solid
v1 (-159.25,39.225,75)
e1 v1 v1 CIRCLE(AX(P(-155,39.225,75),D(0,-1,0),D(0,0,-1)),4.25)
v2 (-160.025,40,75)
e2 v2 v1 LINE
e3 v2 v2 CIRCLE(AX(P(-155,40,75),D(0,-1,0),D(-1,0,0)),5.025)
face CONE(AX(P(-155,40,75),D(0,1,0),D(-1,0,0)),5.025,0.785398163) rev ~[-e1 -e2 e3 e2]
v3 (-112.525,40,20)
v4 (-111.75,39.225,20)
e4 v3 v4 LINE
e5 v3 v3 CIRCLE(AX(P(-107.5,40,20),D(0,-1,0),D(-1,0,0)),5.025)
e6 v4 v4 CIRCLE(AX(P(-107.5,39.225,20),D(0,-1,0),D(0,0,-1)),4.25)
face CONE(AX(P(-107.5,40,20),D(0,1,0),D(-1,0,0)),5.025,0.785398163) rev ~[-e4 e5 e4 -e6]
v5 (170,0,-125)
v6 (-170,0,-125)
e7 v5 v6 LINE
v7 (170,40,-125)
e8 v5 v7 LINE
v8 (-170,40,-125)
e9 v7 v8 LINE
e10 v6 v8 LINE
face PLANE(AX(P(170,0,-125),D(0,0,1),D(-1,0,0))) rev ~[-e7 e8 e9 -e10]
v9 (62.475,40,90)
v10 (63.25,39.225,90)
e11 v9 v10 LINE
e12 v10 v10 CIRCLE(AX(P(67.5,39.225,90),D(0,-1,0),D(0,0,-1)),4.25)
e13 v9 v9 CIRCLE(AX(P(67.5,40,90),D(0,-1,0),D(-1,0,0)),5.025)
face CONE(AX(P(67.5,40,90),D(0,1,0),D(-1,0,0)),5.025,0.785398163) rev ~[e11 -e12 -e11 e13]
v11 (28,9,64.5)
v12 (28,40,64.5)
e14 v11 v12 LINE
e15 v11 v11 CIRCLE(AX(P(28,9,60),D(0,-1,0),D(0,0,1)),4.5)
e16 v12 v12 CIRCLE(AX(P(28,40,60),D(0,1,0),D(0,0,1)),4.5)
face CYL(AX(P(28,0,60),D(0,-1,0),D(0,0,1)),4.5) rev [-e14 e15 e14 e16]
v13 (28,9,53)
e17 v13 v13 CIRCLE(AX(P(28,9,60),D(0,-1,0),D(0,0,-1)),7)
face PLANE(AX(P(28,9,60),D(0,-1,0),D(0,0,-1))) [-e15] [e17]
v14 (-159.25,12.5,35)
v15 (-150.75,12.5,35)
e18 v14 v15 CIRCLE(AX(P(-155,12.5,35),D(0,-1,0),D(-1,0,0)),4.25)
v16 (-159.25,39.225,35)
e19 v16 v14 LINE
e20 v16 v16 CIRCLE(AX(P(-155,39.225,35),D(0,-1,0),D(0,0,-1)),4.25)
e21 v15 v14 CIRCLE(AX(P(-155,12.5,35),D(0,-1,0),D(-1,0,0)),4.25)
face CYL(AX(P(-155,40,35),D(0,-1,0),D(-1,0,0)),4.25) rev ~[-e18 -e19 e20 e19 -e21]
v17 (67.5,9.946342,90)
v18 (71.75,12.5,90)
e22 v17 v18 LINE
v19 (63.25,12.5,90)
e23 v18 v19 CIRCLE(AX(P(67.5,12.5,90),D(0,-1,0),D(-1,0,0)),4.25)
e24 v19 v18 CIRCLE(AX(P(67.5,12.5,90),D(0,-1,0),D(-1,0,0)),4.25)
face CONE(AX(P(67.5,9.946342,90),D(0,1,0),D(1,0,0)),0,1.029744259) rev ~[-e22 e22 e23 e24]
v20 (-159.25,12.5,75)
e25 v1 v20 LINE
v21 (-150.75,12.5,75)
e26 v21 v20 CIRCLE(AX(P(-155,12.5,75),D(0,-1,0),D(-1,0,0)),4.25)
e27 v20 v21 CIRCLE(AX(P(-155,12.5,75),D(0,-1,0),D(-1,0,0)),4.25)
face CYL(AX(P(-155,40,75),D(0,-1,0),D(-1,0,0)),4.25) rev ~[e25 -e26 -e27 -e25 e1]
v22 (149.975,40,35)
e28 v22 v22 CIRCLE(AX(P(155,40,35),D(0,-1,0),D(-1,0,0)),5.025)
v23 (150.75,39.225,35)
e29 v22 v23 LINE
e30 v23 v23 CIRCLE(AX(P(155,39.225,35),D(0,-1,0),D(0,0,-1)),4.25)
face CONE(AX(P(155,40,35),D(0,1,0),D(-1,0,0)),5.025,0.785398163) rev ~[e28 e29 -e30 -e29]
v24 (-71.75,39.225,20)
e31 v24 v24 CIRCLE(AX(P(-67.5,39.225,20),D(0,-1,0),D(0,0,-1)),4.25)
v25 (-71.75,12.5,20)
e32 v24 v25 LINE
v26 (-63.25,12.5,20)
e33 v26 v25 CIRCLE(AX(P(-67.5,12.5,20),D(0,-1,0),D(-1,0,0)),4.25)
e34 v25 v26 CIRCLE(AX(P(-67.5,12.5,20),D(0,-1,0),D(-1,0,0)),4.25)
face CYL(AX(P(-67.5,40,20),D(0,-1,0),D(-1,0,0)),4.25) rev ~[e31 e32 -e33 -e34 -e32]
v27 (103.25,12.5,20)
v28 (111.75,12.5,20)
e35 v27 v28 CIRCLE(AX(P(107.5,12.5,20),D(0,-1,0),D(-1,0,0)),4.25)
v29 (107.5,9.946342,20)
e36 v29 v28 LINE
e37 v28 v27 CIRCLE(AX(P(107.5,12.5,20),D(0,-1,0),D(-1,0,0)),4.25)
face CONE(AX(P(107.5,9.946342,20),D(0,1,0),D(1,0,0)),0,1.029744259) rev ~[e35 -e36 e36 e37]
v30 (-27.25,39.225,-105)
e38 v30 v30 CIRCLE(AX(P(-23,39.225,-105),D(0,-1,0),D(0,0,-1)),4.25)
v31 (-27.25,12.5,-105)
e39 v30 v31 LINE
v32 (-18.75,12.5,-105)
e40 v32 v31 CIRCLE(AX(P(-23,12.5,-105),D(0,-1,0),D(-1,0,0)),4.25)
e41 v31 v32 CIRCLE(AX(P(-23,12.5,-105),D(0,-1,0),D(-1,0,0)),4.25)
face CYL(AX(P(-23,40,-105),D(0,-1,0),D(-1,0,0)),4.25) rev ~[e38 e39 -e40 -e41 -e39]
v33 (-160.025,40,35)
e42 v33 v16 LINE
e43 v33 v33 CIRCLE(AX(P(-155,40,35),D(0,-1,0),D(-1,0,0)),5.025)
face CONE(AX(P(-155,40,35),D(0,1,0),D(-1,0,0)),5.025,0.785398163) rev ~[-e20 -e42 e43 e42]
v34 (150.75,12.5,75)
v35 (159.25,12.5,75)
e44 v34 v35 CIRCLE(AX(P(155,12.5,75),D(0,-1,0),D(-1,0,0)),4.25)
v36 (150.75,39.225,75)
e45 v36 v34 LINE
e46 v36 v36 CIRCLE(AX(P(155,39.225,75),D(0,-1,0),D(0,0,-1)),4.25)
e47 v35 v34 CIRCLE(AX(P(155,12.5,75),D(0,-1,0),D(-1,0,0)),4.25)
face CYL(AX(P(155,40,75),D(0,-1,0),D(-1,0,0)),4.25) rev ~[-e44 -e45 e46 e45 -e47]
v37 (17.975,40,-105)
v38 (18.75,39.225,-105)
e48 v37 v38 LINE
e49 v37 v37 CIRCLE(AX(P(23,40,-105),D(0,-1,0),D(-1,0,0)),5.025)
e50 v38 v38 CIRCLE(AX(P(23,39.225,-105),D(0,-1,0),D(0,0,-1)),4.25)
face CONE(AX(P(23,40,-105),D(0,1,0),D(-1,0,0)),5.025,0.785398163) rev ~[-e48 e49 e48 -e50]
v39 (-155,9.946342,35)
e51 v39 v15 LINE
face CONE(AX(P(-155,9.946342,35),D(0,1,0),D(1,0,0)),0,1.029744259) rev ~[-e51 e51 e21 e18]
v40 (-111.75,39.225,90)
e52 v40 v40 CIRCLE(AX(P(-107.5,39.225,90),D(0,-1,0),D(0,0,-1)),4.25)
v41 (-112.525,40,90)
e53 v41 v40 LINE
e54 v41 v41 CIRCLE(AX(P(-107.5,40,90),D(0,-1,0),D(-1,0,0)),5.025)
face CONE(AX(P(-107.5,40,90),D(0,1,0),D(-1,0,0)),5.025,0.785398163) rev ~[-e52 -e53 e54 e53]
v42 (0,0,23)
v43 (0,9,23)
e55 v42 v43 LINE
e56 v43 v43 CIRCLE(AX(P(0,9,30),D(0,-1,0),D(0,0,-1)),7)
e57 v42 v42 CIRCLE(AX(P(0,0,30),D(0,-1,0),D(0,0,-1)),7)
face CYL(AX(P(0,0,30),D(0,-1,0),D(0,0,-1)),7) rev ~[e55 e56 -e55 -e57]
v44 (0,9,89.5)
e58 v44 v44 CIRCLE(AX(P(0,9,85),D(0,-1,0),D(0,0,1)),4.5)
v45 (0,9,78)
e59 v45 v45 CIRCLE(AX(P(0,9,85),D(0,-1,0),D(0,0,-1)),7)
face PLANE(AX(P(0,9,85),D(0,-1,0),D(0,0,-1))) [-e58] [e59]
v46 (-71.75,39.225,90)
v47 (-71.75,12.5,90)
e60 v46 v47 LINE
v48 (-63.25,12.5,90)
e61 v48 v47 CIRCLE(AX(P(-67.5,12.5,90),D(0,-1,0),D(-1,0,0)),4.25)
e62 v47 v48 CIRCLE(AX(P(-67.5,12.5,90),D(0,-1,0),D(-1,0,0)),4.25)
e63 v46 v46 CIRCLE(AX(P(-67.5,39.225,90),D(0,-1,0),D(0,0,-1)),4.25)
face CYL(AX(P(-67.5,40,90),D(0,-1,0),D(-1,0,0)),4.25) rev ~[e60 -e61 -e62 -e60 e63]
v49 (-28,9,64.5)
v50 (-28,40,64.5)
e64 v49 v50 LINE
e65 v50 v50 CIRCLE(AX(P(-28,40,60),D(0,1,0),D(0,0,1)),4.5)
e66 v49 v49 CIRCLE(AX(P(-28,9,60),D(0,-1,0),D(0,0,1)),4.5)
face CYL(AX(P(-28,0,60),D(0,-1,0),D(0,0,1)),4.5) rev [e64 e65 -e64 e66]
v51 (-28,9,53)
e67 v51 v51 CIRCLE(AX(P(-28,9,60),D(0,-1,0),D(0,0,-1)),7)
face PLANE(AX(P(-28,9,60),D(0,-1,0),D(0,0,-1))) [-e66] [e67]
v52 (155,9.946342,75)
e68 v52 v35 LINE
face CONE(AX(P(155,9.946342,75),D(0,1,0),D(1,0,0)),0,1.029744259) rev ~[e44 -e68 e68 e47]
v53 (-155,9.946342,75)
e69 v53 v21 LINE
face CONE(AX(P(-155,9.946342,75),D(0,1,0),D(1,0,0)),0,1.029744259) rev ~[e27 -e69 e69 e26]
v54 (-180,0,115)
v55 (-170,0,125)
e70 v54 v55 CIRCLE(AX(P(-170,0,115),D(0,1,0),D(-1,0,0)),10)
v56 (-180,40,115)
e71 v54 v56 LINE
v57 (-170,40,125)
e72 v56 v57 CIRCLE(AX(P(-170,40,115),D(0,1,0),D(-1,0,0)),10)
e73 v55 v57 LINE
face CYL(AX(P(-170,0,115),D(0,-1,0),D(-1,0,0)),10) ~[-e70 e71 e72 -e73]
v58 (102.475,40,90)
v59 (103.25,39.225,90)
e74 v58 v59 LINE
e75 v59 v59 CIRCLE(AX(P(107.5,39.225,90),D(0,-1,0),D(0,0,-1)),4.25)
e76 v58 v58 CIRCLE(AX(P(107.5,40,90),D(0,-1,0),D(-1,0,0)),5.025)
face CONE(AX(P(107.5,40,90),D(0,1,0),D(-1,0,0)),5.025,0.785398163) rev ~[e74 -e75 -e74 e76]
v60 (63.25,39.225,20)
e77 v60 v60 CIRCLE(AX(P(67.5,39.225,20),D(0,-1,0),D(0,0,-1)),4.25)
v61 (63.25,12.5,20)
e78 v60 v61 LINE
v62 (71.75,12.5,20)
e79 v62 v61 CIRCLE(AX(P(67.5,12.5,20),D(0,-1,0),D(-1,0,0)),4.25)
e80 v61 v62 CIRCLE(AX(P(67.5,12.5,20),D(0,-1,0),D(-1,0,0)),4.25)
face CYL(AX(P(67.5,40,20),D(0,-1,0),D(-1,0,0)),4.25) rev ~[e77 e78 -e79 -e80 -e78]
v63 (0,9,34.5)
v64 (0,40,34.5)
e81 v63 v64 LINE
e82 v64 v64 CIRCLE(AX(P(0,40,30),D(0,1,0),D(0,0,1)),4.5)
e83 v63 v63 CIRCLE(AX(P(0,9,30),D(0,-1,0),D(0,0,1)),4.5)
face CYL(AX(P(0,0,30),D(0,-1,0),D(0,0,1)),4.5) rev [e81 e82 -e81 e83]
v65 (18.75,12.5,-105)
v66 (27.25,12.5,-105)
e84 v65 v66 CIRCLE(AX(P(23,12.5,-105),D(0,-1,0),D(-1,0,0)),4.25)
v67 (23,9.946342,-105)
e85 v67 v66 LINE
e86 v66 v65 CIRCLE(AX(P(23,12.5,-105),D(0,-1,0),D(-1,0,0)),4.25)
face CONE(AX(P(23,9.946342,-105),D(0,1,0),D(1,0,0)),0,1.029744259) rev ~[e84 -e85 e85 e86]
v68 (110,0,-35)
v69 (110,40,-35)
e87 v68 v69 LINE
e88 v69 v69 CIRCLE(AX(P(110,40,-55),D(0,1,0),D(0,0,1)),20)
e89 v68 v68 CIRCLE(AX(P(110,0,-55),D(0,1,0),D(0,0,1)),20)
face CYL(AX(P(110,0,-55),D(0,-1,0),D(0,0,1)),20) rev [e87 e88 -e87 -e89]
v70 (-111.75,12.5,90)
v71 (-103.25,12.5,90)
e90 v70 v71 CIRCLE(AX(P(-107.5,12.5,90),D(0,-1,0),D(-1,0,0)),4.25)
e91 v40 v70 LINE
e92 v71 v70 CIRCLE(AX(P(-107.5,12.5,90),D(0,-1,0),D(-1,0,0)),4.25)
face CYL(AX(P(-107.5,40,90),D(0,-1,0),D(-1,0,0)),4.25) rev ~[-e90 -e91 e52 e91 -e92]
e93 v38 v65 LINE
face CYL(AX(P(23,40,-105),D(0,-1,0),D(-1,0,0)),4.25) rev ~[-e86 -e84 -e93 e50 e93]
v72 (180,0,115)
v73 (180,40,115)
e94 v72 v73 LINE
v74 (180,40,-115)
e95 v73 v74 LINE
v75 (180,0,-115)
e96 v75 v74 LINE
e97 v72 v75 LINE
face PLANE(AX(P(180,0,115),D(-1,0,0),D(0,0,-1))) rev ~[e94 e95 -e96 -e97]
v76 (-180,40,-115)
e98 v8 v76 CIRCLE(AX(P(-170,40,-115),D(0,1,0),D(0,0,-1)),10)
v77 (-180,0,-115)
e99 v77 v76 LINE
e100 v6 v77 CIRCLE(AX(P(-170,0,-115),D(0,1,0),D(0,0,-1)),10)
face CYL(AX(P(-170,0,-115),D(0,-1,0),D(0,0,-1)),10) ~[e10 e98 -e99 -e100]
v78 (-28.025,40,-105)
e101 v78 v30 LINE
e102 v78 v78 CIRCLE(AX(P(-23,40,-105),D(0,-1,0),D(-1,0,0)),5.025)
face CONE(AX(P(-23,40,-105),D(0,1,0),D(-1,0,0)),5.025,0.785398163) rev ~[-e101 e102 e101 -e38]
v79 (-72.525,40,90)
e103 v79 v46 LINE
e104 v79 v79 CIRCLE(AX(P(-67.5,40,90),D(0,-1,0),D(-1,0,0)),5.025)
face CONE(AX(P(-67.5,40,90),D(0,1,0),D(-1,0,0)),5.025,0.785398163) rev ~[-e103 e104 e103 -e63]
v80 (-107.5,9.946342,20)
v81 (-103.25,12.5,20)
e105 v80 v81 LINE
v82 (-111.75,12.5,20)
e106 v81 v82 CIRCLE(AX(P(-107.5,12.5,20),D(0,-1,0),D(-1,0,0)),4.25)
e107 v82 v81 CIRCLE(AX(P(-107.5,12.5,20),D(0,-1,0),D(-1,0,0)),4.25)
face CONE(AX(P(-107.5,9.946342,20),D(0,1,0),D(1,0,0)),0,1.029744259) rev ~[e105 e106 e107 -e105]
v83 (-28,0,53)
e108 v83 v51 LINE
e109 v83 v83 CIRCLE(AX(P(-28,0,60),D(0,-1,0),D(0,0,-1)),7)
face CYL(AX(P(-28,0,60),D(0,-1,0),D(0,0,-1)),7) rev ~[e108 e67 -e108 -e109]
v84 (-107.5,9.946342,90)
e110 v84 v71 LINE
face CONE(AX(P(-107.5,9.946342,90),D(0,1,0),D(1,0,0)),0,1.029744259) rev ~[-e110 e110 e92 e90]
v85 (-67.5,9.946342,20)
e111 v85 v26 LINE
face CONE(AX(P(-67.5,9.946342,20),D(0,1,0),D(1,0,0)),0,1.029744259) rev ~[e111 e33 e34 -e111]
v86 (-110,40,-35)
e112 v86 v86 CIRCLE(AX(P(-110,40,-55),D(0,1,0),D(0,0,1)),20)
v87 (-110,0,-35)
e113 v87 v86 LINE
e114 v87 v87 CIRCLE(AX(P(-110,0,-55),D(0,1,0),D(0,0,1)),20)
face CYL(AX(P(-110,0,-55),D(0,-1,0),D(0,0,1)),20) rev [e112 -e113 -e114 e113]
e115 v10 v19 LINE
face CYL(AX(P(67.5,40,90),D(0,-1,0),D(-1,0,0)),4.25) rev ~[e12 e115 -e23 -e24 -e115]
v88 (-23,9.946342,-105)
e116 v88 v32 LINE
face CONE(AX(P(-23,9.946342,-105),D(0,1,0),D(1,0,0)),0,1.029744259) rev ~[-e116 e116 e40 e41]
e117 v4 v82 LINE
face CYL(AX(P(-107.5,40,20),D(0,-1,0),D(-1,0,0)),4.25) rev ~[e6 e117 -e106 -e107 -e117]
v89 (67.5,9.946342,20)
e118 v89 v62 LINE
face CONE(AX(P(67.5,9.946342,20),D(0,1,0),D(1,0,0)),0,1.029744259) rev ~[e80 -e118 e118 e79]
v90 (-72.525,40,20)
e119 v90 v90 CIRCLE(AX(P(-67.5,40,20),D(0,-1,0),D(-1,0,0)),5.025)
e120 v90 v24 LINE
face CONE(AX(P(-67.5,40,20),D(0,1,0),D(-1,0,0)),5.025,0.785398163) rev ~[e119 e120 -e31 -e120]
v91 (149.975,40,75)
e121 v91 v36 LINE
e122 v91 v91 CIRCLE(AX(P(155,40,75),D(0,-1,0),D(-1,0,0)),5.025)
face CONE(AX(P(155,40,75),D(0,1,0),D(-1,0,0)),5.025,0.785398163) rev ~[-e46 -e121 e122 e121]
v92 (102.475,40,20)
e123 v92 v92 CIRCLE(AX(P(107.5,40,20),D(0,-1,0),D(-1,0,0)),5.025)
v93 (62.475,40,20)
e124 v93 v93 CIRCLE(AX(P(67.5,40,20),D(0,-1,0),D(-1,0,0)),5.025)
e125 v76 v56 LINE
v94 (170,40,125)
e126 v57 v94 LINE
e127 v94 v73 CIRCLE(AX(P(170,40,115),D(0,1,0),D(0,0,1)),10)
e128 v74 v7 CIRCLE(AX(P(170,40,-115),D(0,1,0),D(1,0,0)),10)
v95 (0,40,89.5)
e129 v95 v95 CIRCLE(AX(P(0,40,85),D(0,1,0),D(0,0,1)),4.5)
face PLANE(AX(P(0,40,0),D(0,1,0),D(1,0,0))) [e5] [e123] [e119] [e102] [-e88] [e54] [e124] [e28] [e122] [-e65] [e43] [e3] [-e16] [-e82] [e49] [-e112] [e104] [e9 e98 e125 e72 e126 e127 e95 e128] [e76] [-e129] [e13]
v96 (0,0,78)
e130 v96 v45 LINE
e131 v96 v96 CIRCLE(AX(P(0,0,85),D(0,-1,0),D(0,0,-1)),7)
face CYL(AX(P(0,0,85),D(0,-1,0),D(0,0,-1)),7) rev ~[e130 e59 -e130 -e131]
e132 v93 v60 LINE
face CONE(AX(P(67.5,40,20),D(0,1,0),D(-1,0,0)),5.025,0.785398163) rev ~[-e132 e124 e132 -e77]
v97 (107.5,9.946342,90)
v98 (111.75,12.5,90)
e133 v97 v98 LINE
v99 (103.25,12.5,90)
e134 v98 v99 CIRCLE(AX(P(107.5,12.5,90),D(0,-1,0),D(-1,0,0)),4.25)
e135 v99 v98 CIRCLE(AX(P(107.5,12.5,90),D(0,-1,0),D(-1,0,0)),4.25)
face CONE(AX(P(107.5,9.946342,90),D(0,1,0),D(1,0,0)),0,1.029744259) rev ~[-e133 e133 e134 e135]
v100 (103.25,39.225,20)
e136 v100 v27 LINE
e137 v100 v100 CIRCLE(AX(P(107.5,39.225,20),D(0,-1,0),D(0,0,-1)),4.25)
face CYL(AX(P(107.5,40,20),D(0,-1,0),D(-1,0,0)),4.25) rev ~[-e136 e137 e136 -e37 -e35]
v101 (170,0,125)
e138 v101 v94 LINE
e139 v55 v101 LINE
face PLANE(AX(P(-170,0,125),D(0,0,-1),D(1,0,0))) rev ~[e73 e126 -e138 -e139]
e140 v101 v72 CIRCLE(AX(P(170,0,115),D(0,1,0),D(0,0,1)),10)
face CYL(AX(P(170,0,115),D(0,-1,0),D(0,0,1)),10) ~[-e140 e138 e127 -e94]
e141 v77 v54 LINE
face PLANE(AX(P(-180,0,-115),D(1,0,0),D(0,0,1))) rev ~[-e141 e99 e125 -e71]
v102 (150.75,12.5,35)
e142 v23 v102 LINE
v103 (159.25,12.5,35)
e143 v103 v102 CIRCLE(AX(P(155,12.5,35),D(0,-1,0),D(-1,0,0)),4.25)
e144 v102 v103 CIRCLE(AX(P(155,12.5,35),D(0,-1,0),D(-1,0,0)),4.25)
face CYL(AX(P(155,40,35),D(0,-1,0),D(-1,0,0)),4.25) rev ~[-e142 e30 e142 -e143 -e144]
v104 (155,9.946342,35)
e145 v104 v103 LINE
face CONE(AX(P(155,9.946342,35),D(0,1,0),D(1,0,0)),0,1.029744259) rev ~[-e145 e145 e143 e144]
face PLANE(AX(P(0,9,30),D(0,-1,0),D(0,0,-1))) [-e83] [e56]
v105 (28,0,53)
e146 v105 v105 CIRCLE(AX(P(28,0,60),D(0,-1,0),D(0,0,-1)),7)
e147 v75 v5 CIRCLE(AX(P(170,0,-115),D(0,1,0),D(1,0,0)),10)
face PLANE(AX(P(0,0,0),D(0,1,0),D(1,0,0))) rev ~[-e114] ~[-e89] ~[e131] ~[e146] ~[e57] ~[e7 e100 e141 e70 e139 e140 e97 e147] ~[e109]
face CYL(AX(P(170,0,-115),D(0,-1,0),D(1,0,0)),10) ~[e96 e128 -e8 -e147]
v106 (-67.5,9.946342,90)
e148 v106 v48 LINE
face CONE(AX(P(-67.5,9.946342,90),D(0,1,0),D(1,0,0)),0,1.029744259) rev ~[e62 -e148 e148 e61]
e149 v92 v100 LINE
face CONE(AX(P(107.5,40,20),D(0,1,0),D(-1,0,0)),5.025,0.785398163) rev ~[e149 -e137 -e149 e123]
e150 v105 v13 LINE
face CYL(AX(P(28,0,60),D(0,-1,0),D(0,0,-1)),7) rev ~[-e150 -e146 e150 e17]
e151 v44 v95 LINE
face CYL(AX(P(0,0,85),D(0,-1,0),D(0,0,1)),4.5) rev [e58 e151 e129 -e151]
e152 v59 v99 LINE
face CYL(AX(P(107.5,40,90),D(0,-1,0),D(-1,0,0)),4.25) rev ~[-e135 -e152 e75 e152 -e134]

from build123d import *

# Parameters (mm, degrees)
SKETCH1_R                    = 20
SKETCH1_R_2                  = 4.5
BOSS_EXTRUDE1_DEPTH          = 40
SKETCH2_R                    = 7
CUT_EXTRUDE1_DEPTH           = 9
M10_TAPPED_HOLE1_D           = 8.5
M10_TAPPED_HOLE1_DEPTH       = 27.5
M10_TAPPED_HOLE1_CSINK_D     = 10.05
M10_TAPPED_HOLE1_CSINK_ANGLE = 90
M10_TAPPED_HOLE1_TIP         = 2.553657631


with BuildPart() as part:
    # Sketch1 → Boss-Extrude1 (new body)
    with BuildSketch(Plane(origin=(0, 0, 0), x_dir=(1, 0, 0), z_dir=(0, 1, 0))):
        with BuildLine():
            Line((-170, -125), (170, -125))
            ThreePointArc((170, -125), (177.071067812, -122.071067812), (180, -115))
            Line((180, -115), (180, 115))
            ThreePointArc((180, 115), (177.071067812, 122.071067812), (170, 125))
            Line((170, 125), (-170, 125))
            ThreePointArc((-170, 125), (-177.071067812, 122.071067812), (-180, 115))
            Line((-180, 115), (-180, -115))
            ThreePointArc((-180, -115), (-177.071067812, -122.071067812), (-170, -125))
        make_face()
        with Locations(Location((-110, 55, 0), (0, 0, 270))):
            Circle(SKETCH1_R, mode=Mode.SUBTRACT)
        with Locations(Location((110, 55, 0), (0, 0, 270))):
            Circle(SKETCH1_R, mode=Mode.SUBTRACT)
        with Locations(Location((0, -85, 0), (0, 0, 270))):
            Circle(SKETCH1_R_2, mode=Mode.SUBTRACT)
        with Locations(Location((0, -30, 0), (0, 0, 270))):
            Circle(SKETCH1_R_2, mode=Mode.SUBTRACT)
        with Locations(Location((28, -60, 0), (0, 0, 270))):
            Circle(SKETCH1_R_2, mode=Mode.SUBTRACT)
        with Locations(Location((-28, -60, 0), (0, 0, 270))):
            Circle(SKETCH1_R_2, mode=Mode.SUBTRACT)
    extrude(amount=BOSS_EXTRUDE1_DEPTH)

    # Sketch2 → Cut-Extrude1 (cut)
    with BuildSketch(Plane.XZ):
        with Locations(Location((0, 30, 0), (0, 0, 270))):
            Circle(SKETCH2_R)
        with Locations(Location((-28, 60, 0), (0, 0, 270))):
            Circle(SKETCH2_R)
        with Locations(Location((0, 85, 0), (0, 0, 270))):
            Circle(SKETCH2_R)
        with Locations(Location((28, 60, 0), (0, 0, 270))):
            Circle(SKETCH2_R)
    extrude(amount=-CUT_EXTRUDE1_DEPTH, mode=Mode.SUBTRACT)

    # M10 Tapped Hole1
    with Locations(Plane(origin=(0, 40, 0), x_dir=(1, 0, 0), z_dir=(0, 1, 0))):
        with Locations((-23, 105), (-155, -35), (-155, -75), (-107.5, -20), (-67.5, -20), (-107.5, -90), (-67.5, -90), (155, -75), (155, -35), (67.5, -90), (107.5, -90), (67.5, -20), (107.5, -20), (23, 105)):
            CounterSinkHole(M10_TAPPED_HOLE1_D / 2, M10_TAPPED_HOLE1_CSINK_D / 2, depth=M10_TAPPED_HOLE1_DEPTH, counter_sink_angle=M10_TAPPED_HOLE1_CSINK_ANGLE)
            with Locations((0, 0, -(M10_TAPPED_HOLE1_DEPTH + M10_TAPPED_HOLE1_TIP / 2))):  # 118° drill point
                Cone(0, M10_TAPPED_HOLE1_D / 2, M10_TAPPED_HOLE1_TIP, mode=Mode.SUBTRACT)


solid = part.part
